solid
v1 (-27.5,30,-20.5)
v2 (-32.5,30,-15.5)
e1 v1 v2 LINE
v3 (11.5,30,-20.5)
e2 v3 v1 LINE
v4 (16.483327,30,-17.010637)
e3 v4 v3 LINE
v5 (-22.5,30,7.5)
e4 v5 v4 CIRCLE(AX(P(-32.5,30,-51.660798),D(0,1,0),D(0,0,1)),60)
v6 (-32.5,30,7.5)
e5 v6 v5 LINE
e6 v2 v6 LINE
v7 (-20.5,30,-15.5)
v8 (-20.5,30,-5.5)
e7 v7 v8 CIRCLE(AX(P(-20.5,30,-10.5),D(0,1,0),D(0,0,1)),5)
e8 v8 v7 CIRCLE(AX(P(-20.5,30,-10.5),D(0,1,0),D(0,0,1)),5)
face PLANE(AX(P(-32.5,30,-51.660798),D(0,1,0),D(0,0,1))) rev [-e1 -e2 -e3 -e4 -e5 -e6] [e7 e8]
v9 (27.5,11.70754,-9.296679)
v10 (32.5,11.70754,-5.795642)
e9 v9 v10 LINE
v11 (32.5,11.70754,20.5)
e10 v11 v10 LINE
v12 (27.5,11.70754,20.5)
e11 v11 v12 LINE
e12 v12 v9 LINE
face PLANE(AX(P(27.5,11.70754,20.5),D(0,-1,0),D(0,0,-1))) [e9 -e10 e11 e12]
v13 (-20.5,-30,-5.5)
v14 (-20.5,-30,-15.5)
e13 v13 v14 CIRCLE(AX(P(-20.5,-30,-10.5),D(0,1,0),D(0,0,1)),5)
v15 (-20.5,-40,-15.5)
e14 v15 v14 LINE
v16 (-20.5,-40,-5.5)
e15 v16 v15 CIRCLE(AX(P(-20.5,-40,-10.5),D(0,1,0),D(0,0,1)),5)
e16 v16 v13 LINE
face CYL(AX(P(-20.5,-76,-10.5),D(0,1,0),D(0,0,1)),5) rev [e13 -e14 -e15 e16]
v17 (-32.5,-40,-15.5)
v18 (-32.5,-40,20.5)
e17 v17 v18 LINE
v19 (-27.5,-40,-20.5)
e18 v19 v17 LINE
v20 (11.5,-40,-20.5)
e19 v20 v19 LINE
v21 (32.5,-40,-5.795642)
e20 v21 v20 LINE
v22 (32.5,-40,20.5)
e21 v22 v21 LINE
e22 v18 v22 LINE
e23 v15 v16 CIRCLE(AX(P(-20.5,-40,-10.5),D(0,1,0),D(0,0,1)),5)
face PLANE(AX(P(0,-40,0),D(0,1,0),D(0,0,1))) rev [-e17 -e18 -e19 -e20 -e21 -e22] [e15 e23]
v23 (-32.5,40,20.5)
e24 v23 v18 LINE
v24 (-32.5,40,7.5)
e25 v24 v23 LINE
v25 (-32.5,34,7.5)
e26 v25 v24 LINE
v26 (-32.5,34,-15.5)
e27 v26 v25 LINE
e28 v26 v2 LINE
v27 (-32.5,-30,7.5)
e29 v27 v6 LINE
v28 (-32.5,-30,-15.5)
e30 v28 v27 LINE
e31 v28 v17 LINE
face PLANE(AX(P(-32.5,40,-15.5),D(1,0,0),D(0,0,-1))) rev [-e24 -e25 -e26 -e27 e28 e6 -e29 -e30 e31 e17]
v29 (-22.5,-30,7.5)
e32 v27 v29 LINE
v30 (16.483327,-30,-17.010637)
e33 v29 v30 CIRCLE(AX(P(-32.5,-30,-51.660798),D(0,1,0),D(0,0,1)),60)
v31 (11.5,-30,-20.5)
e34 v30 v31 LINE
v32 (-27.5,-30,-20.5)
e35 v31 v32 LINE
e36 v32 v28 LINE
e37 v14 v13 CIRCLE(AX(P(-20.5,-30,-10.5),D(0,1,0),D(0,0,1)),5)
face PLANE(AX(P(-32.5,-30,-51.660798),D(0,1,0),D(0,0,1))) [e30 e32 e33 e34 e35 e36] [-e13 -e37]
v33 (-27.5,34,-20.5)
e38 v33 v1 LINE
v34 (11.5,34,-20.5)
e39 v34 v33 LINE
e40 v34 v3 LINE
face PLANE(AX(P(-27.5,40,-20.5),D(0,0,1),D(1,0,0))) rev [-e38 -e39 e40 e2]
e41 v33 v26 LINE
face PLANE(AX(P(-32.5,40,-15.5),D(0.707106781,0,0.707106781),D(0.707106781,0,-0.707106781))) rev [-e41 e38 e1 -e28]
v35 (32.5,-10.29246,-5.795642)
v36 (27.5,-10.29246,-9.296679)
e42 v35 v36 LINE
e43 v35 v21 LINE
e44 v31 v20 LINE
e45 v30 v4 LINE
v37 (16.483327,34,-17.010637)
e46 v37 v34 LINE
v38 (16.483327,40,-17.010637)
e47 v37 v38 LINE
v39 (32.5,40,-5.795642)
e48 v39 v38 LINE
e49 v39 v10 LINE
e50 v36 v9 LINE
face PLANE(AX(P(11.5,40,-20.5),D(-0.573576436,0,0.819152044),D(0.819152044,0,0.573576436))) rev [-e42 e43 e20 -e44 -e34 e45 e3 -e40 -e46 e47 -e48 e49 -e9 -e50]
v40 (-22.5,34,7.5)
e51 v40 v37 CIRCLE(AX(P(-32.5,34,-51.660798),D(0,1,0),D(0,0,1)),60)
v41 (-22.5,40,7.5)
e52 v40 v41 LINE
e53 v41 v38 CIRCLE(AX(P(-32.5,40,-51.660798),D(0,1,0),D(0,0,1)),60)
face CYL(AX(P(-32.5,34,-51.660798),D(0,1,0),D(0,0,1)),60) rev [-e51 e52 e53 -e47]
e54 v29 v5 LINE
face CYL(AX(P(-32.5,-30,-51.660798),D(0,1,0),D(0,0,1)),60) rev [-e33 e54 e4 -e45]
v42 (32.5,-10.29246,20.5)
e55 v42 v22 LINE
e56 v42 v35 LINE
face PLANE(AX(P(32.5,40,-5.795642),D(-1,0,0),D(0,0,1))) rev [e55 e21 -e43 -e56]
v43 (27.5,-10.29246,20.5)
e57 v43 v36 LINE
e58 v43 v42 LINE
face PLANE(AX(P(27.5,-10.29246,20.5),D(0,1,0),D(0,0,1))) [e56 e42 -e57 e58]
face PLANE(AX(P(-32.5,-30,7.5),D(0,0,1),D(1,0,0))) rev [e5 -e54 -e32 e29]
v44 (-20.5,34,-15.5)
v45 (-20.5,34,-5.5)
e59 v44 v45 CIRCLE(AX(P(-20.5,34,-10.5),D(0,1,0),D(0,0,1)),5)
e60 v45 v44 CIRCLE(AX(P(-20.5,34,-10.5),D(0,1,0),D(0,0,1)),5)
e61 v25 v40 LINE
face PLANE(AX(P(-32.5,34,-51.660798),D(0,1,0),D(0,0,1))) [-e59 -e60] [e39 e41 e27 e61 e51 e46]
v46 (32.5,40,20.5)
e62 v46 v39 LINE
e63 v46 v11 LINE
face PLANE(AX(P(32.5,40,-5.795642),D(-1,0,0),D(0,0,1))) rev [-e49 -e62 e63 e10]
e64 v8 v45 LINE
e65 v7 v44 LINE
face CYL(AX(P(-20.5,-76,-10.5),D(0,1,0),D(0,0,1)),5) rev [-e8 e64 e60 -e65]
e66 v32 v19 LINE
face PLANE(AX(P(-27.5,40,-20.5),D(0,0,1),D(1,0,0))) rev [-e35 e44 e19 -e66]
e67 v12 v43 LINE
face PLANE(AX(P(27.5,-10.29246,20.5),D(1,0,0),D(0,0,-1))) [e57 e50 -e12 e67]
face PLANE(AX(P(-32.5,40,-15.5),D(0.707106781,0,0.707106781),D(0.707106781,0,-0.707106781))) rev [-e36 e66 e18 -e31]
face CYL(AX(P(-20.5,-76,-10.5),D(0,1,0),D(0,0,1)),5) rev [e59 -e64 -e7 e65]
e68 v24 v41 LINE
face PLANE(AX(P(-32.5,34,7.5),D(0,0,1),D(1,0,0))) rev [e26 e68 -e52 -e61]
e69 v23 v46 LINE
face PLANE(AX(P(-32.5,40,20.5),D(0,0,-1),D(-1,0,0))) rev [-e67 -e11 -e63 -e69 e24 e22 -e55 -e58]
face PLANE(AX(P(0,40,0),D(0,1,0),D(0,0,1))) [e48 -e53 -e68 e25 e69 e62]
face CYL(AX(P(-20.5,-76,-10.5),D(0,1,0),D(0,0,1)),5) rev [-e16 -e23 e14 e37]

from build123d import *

# Parameters (mm, degrees)
BASE_BLOCK_DEPTH      = 40
SIDE_SLOT_DEPTH       = 56.466205928
SIDE_SLOT_DEPTH_BACK  = 56.466205928
SIDE_SLOT_SKETCH_W    = 5
SIDE_SLOT_SKETCH_H    = 22
TOP_STEP_POCKET_DEPTH = 6
ARC_RELIEF_CUT_DEPTH  = 30
THROUGH_HOLE_SKETCH_R = 5
THROUGH_HOLE_DEPTH    = 110


with BuildPart() as part:
    # Base Block Profile Sketch → Base Block (new, symmetric)
    with BuildSketch(Plane(origin=(0, 0, 0), x_dir=(1, 0, 0), z_dir=(0, 1, 0))):
        Polygon((11.5, 20.5), (32.5, 5.795641698), (32.5, -20.5), (-32.5, -20.5), (-32.5, 15.5), (-27.5, 20.5), align=None)
    extrude(amount=BASE_BLOCK_DEPTH, both=True)

    # Side Slot Sketch → Side Slot (cut, two sides: drawn at the far end of the back side and taken through both)
    with BuildSketch(Plane.XY.offset(-SIDE_SLOT_DEPTH_BACK)):
        with Locations((30, 0.707540159)):
            Rectangle(SIDE_SLOT_SKETCH_W, SIDE_SLOT_SKETCH_H)
    extrude(amount=SIDE_SLOT_DEPTH + SIDE_SLOT_DEPTH_BACK, mode=Mode.SUBTRACT)

    # Top Step Pocket Sketch → Top Step Pocket (cut)
    with BuildSketch(Plane(origin=(0, 40, 0), x_dir=(1, 0, 0), z_dir=(0, 1, 0))):
        with BuildLine():
            Line((16.483327146, 17.010636767), (11.5, 20.5))
            Line((11.5, 20.5), (-27.5, 20.5))
            Line((-27.5, 20.5), (-32.5, 15.5))
            Line((-32.5, 15.5), (-32.5, -7.5))
            Line((-32.5, -7.5), (-22.5, -7.5))
            ThreePointArc((-22.5, -7.5), (-0.563327522, 0.866615575), (16.483327146, 17.010636767))
        make_face()
    extrude(amount=-TOP_STEP_POCKET_DEPTH, mode=Mode.SUBTRACT)

    # Arc Relief Sketch → Arc Relief Cut (cut, symmetric)
    with BuildSketch(Plane(origin=(0, 0, 0), x_dir=(1, 0, 0), z_dir=(0, 1, 0))):
        with BuildLine():
            Line((-27.5, 20.5), (-32.5, 15.5))
            Line((-32.5, 15.5), (-32.5, -7.5))
            Line((-32.5, -7.5), (-22.5, -7.5))
            ThreePointArc((-22.5, -7.5), (-0.563327522, 0.866615575), (16.483327146, 17.010636767))
            Line((16.483327146, 17.010636767), (11.5, 20.5))
            Line((11.5, 20.5), (-27.5, 20.5))
        make_face()
    extrude(amount=ARC_RELIEF_CUT_DEPTH, both=True, mode=Mode.SUBTRACT)

    # Through Hole Sketch → Through Hole (cut)
    with BuildSketch(Plane(origin=(0, 34, 0), x_dir=(1, 0, 0), z_dir=(0, 1, 0))):
        with Locations(Location((-20.5, 10.5, 0), (0, 0, 270))):
            Circle(THROUGH_HOLE_SKETCH_R)
    extrude(amount=-THROUGH_HOLE_DEPTH, mode=Mode.SUBTRACT)


solid = part.part
